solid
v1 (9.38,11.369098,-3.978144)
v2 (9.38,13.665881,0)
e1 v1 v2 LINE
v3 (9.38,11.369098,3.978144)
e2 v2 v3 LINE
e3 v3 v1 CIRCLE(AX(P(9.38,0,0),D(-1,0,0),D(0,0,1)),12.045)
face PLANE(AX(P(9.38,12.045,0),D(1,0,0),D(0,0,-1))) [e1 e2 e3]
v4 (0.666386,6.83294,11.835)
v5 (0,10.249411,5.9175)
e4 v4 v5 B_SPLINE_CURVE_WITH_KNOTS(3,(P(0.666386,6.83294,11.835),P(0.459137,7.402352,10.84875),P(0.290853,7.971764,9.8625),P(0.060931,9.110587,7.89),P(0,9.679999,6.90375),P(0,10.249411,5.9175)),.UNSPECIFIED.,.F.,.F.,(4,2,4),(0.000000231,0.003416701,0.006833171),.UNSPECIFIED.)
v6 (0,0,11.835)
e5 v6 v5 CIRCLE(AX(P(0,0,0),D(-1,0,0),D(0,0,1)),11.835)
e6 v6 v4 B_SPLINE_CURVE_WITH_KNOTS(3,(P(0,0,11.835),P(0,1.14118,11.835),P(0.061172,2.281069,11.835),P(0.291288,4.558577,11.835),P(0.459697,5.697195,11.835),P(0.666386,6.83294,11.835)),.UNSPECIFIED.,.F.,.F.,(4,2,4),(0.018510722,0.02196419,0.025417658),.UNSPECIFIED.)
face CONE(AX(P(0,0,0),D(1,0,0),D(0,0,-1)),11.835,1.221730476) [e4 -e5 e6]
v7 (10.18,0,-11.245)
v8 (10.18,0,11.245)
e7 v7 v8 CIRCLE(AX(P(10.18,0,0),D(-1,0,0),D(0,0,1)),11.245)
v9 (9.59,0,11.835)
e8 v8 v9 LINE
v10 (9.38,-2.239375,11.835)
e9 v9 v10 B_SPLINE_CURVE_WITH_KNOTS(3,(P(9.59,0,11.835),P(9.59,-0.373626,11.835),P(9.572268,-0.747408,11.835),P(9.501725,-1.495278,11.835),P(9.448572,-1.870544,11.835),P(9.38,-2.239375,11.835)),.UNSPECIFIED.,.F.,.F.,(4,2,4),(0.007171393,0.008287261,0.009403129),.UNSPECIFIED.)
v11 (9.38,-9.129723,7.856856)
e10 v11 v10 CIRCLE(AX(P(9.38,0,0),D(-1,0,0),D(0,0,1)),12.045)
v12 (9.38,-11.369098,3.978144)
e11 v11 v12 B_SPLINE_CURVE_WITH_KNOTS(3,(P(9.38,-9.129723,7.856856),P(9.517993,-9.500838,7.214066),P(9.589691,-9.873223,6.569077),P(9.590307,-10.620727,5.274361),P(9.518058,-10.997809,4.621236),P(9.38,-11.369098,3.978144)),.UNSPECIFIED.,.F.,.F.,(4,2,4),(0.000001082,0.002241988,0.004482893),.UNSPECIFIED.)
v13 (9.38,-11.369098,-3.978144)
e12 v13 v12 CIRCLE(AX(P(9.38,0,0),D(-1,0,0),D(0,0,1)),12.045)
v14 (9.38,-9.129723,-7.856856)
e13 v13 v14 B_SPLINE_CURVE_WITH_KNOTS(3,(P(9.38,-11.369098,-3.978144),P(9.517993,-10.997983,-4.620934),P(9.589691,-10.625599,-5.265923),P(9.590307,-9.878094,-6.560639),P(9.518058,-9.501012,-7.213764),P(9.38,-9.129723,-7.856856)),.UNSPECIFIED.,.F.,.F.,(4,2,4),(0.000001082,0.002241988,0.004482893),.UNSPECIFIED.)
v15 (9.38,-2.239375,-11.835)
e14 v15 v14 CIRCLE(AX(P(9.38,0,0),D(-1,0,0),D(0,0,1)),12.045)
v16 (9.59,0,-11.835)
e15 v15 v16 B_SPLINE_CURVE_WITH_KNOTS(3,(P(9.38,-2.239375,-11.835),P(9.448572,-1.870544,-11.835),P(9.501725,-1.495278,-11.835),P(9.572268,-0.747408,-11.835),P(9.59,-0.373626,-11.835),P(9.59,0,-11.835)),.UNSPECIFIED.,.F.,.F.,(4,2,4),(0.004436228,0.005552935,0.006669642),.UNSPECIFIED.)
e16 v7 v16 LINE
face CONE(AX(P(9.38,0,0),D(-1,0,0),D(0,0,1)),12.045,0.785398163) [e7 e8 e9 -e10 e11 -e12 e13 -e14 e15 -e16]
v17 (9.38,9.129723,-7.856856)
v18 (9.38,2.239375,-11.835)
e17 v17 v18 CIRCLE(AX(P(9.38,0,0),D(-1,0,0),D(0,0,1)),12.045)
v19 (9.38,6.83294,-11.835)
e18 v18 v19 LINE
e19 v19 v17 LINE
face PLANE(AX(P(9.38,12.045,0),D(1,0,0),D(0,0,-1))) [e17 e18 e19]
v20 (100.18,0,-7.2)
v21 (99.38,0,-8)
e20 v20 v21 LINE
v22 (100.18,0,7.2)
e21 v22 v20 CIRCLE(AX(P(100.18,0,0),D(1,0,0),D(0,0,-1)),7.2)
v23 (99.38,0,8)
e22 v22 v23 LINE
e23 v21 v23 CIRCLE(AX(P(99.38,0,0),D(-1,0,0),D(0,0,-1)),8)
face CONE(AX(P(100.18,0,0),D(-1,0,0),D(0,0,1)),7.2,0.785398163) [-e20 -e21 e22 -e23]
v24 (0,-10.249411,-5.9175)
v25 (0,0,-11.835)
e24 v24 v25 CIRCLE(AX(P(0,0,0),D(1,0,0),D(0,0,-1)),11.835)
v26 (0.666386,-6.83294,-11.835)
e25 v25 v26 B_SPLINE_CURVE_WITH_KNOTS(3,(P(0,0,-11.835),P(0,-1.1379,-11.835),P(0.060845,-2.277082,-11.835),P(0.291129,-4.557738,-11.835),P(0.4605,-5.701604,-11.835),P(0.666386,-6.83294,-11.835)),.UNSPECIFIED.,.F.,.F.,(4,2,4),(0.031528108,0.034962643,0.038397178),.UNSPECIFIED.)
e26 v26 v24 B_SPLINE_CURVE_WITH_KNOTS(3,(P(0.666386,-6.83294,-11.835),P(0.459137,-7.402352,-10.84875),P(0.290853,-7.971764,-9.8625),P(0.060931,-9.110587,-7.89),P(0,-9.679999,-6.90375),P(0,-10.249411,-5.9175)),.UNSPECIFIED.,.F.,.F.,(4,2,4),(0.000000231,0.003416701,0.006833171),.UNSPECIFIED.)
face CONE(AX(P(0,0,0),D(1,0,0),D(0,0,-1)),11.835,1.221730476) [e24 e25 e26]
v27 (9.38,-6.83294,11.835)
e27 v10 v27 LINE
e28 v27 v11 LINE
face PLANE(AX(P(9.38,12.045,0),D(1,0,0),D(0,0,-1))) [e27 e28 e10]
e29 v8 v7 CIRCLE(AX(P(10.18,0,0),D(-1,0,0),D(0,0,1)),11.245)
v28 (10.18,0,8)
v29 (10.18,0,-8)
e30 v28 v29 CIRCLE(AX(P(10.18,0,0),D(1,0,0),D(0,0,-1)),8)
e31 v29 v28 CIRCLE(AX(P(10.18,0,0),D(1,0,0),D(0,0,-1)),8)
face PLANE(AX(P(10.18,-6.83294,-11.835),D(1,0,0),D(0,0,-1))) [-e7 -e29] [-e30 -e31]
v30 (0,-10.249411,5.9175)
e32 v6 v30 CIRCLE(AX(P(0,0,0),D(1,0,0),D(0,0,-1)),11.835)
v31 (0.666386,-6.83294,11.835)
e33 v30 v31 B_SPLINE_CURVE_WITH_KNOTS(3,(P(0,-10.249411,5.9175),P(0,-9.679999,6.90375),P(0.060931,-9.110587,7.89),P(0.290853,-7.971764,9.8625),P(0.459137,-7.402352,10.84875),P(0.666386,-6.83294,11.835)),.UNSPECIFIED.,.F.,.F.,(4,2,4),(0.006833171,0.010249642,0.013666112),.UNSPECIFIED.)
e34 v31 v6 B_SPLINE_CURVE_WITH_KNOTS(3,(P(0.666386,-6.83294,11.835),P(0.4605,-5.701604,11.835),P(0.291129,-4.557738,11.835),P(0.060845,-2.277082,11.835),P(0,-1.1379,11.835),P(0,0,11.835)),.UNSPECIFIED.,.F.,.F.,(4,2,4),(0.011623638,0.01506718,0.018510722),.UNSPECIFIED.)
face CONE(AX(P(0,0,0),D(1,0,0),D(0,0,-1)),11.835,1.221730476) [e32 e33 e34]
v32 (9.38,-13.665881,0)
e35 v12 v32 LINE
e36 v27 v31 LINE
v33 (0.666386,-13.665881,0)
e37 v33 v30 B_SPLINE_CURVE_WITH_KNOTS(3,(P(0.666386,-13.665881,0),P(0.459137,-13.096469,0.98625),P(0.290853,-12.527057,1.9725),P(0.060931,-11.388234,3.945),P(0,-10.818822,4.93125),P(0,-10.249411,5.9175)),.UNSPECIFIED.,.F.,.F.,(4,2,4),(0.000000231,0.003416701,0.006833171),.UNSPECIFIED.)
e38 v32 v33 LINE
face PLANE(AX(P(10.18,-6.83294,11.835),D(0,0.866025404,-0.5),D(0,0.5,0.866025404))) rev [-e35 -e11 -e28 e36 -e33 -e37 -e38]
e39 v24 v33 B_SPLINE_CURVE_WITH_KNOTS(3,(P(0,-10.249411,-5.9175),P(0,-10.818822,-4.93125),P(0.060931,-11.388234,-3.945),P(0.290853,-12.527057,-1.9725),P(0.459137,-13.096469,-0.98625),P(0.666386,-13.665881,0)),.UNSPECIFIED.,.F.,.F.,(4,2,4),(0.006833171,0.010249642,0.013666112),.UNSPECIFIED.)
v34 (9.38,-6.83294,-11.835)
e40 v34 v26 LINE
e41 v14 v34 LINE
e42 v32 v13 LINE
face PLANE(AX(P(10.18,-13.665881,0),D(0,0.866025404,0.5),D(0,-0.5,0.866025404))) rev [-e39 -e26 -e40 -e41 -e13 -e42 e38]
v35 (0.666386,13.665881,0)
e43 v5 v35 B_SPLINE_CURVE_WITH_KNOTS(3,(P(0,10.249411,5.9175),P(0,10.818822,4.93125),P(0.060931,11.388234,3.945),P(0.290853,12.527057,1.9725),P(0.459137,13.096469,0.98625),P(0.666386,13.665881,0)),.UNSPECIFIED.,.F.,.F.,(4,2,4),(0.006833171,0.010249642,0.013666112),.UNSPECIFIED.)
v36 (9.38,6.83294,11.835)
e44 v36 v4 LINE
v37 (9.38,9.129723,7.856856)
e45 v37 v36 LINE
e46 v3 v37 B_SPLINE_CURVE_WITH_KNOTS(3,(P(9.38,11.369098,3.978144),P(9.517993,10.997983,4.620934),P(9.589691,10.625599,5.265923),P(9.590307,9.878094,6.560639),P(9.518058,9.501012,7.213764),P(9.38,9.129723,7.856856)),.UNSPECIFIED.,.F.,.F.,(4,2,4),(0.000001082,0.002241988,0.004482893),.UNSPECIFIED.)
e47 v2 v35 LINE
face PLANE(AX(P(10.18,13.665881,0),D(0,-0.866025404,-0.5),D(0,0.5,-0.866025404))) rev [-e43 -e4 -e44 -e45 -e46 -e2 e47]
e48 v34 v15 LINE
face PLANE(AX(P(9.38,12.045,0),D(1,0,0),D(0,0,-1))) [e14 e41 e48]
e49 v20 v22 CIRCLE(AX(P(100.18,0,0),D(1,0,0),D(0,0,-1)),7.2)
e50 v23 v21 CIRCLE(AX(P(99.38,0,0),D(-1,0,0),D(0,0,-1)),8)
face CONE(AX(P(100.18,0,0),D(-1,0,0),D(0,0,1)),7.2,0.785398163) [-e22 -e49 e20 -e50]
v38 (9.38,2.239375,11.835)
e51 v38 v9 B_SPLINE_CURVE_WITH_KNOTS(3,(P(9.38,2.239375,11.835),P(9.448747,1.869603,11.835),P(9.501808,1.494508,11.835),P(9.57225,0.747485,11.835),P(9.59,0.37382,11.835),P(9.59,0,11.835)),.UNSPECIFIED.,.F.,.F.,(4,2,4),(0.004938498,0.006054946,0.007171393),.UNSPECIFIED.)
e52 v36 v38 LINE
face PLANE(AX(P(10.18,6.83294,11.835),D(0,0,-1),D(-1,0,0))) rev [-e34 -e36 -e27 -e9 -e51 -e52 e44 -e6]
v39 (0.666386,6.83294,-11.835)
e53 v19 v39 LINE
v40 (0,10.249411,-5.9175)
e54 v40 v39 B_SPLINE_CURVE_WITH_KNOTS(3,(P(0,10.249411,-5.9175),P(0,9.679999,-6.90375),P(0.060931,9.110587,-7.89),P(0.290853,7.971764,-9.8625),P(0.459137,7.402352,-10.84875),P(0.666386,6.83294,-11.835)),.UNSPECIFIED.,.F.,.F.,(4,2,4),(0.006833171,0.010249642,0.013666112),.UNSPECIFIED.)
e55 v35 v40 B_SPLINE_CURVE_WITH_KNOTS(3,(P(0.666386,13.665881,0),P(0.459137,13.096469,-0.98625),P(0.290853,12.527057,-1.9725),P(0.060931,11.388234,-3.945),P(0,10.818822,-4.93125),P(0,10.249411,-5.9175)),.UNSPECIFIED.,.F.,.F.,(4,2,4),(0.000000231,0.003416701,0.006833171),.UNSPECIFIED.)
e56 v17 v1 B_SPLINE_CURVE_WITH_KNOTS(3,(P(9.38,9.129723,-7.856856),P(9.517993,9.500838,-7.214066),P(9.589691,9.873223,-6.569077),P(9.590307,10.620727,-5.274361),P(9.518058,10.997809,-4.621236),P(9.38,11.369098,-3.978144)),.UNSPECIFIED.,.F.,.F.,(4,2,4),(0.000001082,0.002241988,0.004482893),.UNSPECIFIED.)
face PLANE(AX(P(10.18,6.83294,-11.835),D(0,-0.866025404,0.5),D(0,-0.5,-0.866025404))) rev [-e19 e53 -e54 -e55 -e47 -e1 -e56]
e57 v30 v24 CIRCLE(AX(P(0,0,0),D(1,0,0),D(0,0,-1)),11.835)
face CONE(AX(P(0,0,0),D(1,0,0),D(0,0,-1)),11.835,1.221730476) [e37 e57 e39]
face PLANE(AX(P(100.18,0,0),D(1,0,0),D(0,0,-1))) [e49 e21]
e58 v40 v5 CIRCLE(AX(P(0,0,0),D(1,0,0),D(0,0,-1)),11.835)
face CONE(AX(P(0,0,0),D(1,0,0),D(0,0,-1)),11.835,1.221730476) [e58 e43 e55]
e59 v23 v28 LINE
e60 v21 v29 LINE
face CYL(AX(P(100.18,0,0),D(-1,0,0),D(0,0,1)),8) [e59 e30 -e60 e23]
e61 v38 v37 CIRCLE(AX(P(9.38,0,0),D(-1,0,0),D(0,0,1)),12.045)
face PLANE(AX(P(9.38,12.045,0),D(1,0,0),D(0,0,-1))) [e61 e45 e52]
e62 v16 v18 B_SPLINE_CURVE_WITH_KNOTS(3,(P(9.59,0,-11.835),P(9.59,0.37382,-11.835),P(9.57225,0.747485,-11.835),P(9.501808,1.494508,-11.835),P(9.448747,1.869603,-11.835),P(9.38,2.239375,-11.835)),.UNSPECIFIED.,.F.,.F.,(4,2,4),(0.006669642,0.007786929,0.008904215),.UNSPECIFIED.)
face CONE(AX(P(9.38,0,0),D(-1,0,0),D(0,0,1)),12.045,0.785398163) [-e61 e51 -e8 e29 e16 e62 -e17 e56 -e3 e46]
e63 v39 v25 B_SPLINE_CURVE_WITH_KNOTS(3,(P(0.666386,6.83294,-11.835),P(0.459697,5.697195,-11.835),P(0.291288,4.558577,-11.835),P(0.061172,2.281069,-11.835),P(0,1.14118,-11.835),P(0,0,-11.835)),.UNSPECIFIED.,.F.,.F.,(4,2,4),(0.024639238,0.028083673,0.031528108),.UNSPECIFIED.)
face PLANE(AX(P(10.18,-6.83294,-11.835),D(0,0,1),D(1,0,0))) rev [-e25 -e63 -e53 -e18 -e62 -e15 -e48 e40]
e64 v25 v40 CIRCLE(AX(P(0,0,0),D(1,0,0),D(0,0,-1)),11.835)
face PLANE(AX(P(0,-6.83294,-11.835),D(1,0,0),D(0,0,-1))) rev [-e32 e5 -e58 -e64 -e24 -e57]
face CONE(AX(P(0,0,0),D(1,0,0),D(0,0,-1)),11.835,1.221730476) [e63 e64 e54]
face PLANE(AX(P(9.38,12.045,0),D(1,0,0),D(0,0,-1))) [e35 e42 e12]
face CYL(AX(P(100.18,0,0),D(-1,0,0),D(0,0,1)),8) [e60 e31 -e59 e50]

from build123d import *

# Parameters (mm, degrees)
BASEHEAD_DEPTH = 10.18
SKETCH5_R      = 8
BASEBODY_DEPTH = 90
CHAMFER1_SIZE  = 0.8


with BuildPart() as part:
    # Sketch2 → BaseHead (new body)
    with BuildSketch(Plane(origin=(0, 0, 0), x_dir=(0, 0, -1), z_dir=(1, 0, 0))):
        Polygon((11.835, -6.832940436), (11.835, 6.832940436), (0, 13.665880872), (-11.835, 6.832940436), (-11.835, -6.832940436), (0, -13.665880872), align=None)
    extrude(amount=BASEHEAD_DEPTH)

    # Sketch3 → BearingFace (revolve, cut)
    with BuildSketch(Plane.XY, mode=Mode.PRIVATE) as bearingface_sk:
        Polygon((10.18, 13.665880872), (10.18, 11.245), (9.38, 12.045), (9.38, 13.665880872), align=None)
    revolve(bearingface_sk.sketch.rotate(Axis((-0.957090588, 0, 0), (1, 0, 0)), 90), axis=Axis((-0.957090588, 0, 0), (1, 0, 0)), mode=Mode.SUBTRACT)

    # Sketch4 → Head chamfer (revolve, cut)
    with BuildSketch(Plane.XY):
        Polygon((0, 13.665880872), (0.66638614, 13.665880872), (0, 11.835), align=None)
    revolve(axis=Axis((-0.493528746, 0, 0), (1, 0, 0)), mode=Mode.SUBTRACT)

    # Sketch5 → BaseBody (add)
    with BuildSketch(Plane(origin=(10.18, 0, 0), x_dir=(0, 0, -1), z_dir=(1, 0, 0))):
        with Locations(Location((0, 0, 0), (0, 0, 180))):
            Circle(SKETCH5_R)
    extrude(amount=BASEBODY_DEPTH)

    # Chamfer1
    chamfer1_edges = [part.edges().sort_by_distance(p)[0] for p in [
        (100.18, 0, -8),
    ]]
    chamfer(chamfer1_edges, length=CHAMFER1_SIZE)


solid = part.part
